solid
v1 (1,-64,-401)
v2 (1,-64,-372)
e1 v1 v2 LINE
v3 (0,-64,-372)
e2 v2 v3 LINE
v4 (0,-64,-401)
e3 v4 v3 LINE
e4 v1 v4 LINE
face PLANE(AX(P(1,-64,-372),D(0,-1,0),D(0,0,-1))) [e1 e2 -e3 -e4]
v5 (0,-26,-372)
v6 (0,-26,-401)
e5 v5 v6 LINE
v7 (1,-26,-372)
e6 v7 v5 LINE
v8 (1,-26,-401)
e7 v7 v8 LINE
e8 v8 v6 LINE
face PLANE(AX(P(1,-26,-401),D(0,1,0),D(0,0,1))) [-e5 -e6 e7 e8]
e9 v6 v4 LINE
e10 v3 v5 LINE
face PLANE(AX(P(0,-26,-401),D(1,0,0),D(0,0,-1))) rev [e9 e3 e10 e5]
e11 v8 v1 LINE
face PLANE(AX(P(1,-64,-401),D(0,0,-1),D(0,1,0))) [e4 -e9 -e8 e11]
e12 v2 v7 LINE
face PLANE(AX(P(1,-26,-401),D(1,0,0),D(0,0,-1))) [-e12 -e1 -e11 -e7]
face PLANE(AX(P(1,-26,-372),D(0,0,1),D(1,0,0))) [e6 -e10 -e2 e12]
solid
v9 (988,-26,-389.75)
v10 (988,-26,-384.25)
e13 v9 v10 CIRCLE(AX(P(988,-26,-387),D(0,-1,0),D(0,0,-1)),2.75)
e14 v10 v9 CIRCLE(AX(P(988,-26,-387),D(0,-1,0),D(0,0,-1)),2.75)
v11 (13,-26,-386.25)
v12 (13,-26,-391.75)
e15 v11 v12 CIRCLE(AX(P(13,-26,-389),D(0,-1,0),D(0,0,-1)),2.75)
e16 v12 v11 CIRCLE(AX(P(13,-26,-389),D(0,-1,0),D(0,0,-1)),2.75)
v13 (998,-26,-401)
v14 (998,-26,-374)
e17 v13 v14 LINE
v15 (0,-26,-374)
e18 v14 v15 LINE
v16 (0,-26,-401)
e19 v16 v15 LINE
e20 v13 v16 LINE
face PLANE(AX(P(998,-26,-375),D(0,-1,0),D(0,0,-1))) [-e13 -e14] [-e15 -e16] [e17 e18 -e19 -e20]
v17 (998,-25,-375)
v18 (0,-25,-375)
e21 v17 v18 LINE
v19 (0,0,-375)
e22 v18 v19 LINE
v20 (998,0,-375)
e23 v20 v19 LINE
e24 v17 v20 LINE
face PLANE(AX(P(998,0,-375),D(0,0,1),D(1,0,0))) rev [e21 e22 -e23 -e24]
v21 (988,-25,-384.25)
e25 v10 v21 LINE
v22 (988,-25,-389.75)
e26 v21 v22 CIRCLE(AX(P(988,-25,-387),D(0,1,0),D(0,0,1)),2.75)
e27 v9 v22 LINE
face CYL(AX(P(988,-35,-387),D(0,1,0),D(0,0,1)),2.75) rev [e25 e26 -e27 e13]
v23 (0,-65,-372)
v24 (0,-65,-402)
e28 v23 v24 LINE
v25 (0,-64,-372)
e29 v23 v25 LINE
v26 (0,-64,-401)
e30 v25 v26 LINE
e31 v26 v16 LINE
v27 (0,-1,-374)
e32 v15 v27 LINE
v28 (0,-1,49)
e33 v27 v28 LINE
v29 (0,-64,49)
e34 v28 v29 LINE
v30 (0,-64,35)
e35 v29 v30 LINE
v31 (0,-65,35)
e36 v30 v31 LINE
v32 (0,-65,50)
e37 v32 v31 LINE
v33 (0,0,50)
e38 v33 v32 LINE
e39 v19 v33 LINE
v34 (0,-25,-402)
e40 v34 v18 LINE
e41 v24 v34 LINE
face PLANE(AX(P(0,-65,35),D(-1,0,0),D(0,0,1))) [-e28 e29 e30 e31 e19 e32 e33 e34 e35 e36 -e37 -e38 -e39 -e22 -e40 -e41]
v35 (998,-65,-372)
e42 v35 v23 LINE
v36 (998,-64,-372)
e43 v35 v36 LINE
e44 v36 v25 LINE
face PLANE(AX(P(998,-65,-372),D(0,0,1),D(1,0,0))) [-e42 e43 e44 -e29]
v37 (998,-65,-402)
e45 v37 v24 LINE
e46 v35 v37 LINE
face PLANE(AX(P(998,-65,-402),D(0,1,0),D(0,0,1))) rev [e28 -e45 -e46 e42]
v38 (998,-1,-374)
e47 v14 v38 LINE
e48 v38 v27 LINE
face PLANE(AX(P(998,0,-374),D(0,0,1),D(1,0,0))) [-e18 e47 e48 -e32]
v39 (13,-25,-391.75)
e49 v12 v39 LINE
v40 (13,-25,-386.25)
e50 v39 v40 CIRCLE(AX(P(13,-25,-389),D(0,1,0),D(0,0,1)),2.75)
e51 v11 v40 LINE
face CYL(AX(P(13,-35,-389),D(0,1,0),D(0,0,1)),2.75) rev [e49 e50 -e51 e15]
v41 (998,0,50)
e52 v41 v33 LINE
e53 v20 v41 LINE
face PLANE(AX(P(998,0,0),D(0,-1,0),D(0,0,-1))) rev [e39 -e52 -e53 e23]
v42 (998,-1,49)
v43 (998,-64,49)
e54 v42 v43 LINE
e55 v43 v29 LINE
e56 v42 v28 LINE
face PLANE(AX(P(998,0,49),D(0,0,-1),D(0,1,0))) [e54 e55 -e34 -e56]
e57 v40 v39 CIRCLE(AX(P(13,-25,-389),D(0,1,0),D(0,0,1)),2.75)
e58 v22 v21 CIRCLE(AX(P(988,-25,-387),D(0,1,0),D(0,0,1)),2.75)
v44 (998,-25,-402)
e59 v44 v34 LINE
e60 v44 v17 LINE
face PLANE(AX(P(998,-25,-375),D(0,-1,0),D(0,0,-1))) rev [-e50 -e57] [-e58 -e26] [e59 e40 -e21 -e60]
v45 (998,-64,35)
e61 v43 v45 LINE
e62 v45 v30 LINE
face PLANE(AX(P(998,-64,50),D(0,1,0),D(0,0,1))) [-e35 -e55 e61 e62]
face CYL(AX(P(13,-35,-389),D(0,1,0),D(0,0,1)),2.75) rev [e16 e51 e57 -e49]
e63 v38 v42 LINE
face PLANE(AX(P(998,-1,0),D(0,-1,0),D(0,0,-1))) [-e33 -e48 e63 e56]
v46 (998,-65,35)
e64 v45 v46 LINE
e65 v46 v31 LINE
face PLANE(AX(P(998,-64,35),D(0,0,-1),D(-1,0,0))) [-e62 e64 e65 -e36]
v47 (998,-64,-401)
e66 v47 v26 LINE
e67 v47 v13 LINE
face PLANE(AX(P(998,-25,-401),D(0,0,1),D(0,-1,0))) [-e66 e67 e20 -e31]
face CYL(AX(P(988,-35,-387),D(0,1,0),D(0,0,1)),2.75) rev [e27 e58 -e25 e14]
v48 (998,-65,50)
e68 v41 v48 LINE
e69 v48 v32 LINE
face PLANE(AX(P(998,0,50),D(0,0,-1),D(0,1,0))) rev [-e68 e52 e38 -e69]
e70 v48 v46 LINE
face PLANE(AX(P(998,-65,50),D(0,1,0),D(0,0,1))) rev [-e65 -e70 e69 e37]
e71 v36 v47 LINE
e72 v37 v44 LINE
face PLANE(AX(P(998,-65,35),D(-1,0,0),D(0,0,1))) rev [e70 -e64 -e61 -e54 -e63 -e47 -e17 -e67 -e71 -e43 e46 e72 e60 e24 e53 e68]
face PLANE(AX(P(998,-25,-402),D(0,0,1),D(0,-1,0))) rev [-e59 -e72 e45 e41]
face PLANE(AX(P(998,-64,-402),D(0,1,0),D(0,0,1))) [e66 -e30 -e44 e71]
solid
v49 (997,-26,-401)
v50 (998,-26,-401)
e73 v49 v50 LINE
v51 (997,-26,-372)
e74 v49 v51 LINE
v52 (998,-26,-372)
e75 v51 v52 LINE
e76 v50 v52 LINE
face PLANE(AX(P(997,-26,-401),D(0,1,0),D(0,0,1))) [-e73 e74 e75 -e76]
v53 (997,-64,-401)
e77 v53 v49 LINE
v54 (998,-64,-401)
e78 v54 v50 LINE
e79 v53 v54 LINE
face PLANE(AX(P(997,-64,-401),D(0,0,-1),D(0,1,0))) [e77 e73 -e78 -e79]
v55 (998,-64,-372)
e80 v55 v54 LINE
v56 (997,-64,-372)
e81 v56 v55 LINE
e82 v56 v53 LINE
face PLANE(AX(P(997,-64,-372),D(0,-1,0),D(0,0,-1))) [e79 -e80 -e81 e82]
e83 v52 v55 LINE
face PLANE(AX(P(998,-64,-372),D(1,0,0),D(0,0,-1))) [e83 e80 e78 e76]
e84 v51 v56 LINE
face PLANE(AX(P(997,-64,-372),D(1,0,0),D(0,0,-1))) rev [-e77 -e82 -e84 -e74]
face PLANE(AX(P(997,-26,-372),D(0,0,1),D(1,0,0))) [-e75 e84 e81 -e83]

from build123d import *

# Parameters (mm, degrees)
EXTRUDE_THIN1_DEPTH = 998
SKETCH4_W           = 29
SKETCH4_H           = 38
EXTRUDE2_DEPTH      = 1
SKETCH5_W           = 29
SKETCH5_H           = 38
EXTRUDE3_DEPTH      = 1
SKETCH6_R           = 2.75
CUT_EXTRUDE1_DEPTH  = 10


with BuildPart() as part:
    # Sketch1 → Extrude-Thin1 (new body)
    with BuildSketch(Plane(origin=(0, 0, 0), x_dir=(0, 0, -1), z_dir=(1, 0, 0))):
        Polygon((-35, -65), (-50, -65), (-50, 0), (0, 0), (375, 0), (375, -25), (402, -25), (402, -65), (372, -65), (372, -64), (401, -64), (401, -26), (374, -26), (374, -1), (0, -1), (-49, -1), (-49, -64), (-35, -64), align=None)
    extrude(amount=EXTRUDE_THIN1_DEPTH)

    # Sketch6 → Cut-Extrude1 (cut)
    with BuildSketch(Plane(origin=(0, -25, 0), x_dir=(1, 0, 0), z_dir=(0, 1, 0))):
        with Locations(Location((13, 389, 0), (0, 0, 270))):
            Circle(SKETCH6_R)
        with Locations(Location((988, 387, 0), (0, 0, 270))):
            Circle(SKETCH6_R)
    extrude(amount=-CUT_EXTRUDE1_DEPTH, mode=Mode.SUBTRACT)


with BuildPart() as body_2:
    # Sketch4 → Extrude2 (new body)
    with BuildSketch(Plane.ZY):
        with Locations((-386.5, -45)):
            Rectangle(SKETCH4_W, SKETCH4_H)
    extrude(amount=-EXTRUDE2_DEPTH)


with BuildPart() as body_3:
    # Sketch5 → Extrude3 (new body)
    with BuildSketch(Plane(origin=(998, 0, 0), x_dir=(0, 0, -1), z_dir=(1, 0, 0))):
        with Locations((386.5, -45)):
            Rectangle(SKETCH5_W, SKETCH5_H)
    extrude(amount=-EXTRUDE3_DEPTH)


solid = Compound([part.part, body_2.part, body_3.part])
